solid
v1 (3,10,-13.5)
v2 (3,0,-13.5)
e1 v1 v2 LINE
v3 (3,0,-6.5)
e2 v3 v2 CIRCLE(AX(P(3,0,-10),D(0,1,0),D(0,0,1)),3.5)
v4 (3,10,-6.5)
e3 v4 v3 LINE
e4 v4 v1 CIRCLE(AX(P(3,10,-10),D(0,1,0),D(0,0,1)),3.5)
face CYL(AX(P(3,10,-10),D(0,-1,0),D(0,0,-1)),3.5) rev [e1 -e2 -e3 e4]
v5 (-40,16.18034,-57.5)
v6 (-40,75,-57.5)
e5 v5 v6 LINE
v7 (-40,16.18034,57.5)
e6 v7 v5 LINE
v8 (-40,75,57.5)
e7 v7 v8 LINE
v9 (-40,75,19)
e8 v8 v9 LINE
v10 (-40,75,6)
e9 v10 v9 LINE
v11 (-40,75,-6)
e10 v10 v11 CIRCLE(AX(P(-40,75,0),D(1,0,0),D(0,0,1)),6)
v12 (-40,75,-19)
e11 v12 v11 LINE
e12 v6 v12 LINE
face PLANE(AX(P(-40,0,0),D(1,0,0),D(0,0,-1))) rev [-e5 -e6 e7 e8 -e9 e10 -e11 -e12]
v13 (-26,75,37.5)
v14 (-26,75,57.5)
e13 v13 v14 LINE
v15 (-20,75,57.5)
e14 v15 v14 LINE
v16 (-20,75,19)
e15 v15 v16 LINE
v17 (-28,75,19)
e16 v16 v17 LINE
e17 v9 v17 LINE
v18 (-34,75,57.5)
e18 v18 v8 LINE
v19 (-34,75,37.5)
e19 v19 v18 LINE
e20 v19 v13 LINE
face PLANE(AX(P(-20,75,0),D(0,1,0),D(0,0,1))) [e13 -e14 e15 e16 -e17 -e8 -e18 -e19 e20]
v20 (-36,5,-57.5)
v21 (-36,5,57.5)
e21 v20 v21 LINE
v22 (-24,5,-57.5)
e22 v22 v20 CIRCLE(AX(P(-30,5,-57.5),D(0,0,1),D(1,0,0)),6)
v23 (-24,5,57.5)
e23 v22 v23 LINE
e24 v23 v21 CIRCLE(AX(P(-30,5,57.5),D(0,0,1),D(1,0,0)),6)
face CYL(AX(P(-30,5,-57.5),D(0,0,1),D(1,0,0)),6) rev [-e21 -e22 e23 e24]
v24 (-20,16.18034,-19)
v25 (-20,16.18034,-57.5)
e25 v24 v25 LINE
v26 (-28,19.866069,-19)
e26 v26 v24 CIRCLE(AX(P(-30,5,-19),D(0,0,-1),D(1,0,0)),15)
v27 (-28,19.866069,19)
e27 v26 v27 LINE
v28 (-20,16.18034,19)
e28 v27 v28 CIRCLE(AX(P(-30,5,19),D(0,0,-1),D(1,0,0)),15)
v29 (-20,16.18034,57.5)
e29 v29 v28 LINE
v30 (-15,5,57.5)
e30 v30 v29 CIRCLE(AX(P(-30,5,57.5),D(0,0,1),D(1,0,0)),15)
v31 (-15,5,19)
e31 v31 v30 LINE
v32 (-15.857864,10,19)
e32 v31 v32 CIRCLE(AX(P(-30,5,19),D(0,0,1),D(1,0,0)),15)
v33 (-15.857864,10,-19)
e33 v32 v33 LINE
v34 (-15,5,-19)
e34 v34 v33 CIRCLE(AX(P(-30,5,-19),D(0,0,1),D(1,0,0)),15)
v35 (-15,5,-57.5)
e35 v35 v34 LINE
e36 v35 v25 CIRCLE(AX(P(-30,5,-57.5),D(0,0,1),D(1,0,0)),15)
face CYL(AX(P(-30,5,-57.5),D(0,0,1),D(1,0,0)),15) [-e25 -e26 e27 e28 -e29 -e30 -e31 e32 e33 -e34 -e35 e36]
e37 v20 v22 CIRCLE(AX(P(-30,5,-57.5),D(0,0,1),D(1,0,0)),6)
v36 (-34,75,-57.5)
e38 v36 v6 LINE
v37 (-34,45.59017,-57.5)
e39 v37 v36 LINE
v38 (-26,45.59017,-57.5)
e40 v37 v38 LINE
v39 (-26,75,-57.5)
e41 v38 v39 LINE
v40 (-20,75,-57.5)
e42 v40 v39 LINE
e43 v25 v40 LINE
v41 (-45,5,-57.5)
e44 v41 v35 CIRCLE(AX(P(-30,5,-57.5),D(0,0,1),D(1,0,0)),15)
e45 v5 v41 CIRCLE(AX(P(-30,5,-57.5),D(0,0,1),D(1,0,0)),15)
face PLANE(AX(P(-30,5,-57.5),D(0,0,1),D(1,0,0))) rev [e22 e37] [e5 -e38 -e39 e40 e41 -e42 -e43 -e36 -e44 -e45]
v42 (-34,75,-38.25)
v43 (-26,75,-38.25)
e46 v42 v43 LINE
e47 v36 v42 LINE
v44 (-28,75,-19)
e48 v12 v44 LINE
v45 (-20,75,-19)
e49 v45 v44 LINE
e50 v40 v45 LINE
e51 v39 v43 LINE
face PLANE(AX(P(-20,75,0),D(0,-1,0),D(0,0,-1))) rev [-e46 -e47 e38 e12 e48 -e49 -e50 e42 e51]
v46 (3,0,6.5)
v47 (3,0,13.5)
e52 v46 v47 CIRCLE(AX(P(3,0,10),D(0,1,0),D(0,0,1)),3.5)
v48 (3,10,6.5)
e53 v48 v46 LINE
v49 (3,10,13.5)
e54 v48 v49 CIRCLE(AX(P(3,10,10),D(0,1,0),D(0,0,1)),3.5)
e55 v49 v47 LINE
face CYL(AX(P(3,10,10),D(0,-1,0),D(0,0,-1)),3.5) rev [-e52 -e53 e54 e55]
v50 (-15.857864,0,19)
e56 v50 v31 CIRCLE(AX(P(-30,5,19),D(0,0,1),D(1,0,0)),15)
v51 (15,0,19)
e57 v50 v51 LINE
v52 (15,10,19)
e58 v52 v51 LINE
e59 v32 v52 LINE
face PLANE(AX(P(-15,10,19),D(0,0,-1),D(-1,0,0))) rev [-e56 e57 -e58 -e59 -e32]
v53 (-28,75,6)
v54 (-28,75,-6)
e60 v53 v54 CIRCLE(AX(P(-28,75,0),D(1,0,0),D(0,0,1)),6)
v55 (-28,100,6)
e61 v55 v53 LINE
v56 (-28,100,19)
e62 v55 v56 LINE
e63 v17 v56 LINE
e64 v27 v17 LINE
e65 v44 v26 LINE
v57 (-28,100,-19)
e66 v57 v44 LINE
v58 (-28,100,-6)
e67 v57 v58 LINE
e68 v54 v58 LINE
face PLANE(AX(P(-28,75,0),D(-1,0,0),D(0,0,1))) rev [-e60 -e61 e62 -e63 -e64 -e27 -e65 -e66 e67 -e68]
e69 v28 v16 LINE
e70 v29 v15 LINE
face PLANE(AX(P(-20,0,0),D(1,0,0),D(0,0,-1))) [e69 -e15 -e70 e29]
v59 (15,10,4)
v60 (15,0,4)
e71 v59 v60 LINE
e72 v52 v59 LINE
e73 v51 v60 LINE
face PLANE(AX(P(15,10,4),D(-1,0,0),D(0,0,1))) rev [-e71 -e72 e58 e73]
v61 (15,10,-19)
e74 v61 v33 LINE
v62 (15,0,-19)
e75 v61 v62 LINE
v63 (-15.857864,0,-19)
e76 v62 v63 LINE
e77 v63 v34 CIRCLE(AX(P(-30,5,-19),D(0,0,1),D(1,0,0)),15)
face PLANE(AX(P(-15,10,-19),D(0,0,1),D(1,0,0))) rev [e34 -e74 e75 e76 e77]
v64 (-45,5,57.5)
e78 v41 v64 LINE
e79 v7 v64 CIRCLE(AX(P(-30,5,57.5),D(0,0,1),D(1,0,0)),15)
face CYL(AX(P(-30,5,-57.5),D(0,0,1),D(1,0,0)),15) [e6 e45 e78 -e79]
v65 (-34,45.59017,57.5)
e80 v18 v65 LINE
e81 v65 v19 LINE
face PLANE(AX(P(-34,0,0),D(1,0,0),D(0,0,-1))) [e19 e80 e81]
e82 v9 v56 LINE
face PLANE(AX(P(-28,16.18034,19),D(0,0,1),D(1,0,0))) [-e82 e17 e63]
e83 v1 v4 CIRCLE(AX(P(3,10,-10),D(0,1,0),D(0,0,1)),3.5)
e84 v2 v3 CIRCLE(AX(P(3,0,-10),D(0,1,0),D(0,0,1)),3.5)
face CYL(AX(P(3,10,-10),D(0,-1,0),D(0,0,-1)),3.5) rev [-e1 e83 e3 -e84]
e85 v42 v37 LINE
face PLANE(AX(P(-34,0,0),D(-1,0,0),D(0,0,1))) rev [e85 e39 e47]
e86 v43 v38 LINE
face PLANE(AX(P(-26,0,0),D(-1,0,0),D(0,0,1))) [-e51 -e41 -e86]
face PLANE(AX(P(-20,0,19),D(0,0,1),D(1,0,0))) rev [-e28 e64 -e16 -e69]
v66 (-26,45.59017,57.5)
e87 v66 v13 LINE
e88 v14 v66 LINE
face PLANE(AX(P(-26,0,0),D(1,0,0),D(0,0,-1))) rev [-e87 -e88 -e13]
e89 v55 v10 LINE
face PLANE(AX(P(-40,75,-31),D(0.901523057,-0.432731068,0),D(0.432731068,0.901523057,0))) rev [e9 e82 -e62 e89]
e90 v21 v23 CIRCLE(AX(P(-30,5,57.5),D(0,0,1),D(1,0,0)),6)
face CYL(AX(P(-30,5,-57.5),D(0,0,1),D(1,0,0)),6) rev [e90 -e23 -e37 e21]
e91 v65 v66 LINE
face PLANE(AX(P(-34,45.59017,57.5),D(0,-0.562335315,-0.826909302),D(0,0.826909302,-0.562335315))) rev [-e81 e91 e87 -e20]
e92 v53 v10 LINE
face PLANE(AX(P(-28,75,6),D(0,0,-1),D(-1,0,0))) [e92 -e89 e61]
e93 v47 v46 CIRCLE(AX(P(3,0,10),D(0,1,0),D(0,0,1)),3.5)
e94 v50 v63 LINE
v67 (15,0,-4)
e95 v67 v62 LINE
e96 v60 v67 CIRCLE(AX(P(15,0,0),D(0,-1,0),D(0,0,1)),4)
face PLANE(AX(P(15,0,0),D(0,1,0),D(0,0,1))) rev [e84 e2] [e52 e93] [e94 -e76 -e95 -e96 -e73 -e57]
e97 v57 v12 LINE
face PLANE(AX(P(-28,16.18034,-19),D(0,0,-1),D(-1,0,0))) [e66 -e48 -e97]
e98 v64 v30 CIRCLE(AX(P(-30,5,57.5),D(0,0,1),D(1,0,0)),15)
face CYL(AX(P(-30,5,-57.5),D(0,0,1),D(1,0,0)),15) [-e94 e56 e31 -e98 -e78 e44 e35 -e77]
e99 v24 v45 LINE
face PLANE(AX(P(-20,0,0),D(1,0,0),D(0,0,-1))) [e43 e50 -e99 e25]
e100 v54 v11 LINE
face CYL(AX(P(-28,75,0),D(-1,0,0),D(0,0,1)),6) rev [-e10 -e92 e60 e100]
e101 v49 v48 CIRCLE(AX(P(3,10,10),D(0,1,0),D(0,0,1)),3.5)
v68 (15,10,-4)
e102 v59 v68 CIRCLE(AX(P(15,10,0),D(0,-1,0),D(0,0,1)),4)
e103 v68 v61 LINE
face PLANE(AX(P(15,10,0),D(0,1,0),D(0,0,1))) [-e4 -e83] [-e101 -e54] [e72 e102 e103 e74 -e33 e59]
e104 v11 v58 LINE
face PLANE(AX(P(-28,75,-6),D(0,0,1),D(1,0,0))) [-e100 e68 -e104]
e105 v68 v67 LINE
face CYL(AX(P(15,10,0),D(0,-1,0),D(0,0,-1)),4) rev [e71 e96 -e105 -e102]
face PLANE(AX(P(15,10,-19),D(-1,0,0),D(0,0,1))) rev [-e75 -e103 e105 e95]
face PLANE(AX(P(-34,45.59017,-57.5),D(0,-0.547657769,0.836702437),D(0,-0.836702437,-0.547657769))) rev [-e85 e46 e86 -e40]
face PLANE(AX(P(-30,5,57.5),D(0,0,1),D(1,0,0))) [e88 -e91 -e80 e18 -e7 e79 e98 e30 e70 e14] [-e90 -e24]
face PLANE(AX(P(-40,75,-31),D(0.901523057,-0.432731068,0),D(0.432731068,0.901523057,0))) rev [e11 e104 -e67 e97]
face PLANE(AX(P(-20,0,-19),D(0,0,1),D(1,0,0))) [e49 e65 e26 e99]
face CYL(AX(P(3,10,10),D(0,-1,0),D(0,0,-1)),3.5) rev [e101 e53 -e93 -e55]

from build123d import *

# Parameters (mm, degrees)
BASE_FLANGE_SKETCH_R         = 3.5
BASE_FLANGE_DEPTH            = 10
LOCATING_PAD_SKETCH_W        = 38
LOCATING_PAD_SKETCH_H        = 10
LOCATING_PAD_DEPTH           = 10
HINGE_BARREL_SKETCH_R        = 15
HINGE_BARREL_SKETCH_R_2      = 6
HINGE_BARREL_DEPTH           = 76.5
HINGE_START                  = 38.5
BARREL_EXTENSION_SKETCH_R    = 15
BARREL_EXTENSION_SKETCH_R_2  = 6
HINGE_BARREL_EXTENSION_DEPTH = 38.5
PIN_BORE_SKETCH_R            = 6
HINGE_PIN_BORE_12_DEPTH      = 115
GUIDE_WALLS_SKETCH_W         = 38.5
GUIDE_WALLS_SKETCH_H         = 70
GUIDE_WALLS_DEPTH            = 10
CENTRE_FIN_DEPTH             = 12
FIN_V_SLOT_SKETCH_W          = 12
FIN_V_SLOT_SKETCH_H          = 11.180339887
FIN_V_SLOT_DEPTH             = 50
FIN_RELIEF_CUT_DEPTH         = 50
THROUGH_BORE_SKETCH_R        = 6
THROUGH_BORE_12_DEPTH        = 200
WALL_WINDOWS_DEPTH           = 4


with BuildPart() as part:
    # Base Flange Sketch → Base Flange (new body)
    with BuildSketch(Plane(origin=(0, 0, 0), x_dir=(1, 0, 0), z_dir=(0, 1, 0))):
        with BuildLine():
            Line((15, -4), (15, -19))
            Line((15, -19), (-15, -19))
            Line((-15, -19), (-15, 19))
            Line((-15, 19), (15, 19))
            Line((15, 19), (15, 4))
            ThreePointArc((15, 4), (11, 0), (15, -4))
        make_face()
        with Locations(Location((3, 10, 0), (0, 0, 270))):
            Circle(BASE_FLANGE_SKETCH_R, mode=Mode.SUBTRACT)
        with Locations(Location((3, -10, 0), (0, 0, 270))):
            Circle(BASE_FLANGE_SKETCH_R, mode=Mode.SUBTRACT)
    extrude(amount=BASE_FLANGE_DEPTH)

    # Locating Pad Sketch → Locating Pad (add)
    with BuildSketch(Plane.ZY.offset(15)):
        with Locations((0, 5)):
            Rectangle(LOCATING_PAD_SKETCH_W, LOCATING_PAD_SKETCH_H)
    extrude(amount=LOCATING_PAD_DEPTH)

    # Hinge Barrel Sketch → Hinge Barrel (add)
    with BuildSketch(Plane.XY.offset(19)):
        with Locations((-30, 5)):
            Circle(HINGE_BARREL_SKETCH_R)
        with Locations((-30, 5)):
            Circle(HINGE_BARREL_SKETCH_R_2, mode=Mode.SUBTRACT)
    extrude(amount=-HINGE_BARREL_DEPTH)

    # Barrel Extension Sketch → Hinge Barrel Extension (add)
    with BuildSketch(Plane.XY.offset(19).offset(HINGE_START)):
        with Locations((-30, 5)):
            Circle(BARREL_EXTENSION_SKETCH_R)
        with Locations((-30, 5)):
            Circle(BARREL_EXTENSION_SKETCH_R_2, mode=Mode.SUBTRACT)
    extrude(amount=-HINGE_BARREL_EXTENSION_DEPTH)

    # Pin Bore Sketch → Hinge Pin Bore Ø12 (cut)
    with BuildSketch(Plane.XY.offset(57.5)):
        with Locations((-30, 5)):
            Circle(PIN_BORE_SKETCH_R)
    extrude(amount=-HINGE_PIN_BORE_12_DEPTH, mode=Mode.SUBTRACT)

    # Guide Walls Sketch → Guide Walls (add, symmetric)
    with BuildSketch(Plane(origin=(-30, 0, 0), x_dir=(0, 0, -1), z_dir=(1, 0, 0))):
        with Locations((38.25, 40)):
            Rectangle(GUIDE_WALLS_SKETCH_W, GUIDE_WALLS_SKETCH_H)
        with Locations((-38.25, 40)):
            Rectangle(GUIDE_WALLS_SKETCH_W, GUIDE_WALLS_SKETCH_H)
    extrude(amount=GUIDE_WALLS_DEPTH, both=True)

    # Centre Fin Sketch → Centre Fin (add)
    with BuildSketch(Plane.ZY.offset(40)):
        with BuildLine():
            Line((-19, 16.180339887), (19, 16.180339887))
            Line((19, 16.180339887), (19, 111.180339887))
            Line((19, 111.180339887), (6, 111.180339887))
            Line((6, 111.180339887), (6, 75))
            ThreePointArc((6, 75), (0, 69), (-6, 75))
            Line((-6, 75), (-6, 111.180339887))
            Line((-6, 111.180339887), (-19, 111.180339887))
            Line((-19, 111.180339887), (-19, 16.180339887))
        make_face()
    extrude(amount=-CENTRE_FIN_DEPTH)

    # Fin V-Slot Sketch → Fin V-Slot (cut)
    with BuildSketch(Plane.XY.offset(19)):
        with Locations((-34, 105.590169944)):
            Rectangle(FIN_V_SLOT_SKETCH_W, FIN_V_SLOT_SKETCH_H)
    extrude(amount=-FIN_V_SLOT_DEPTH, mode=Mode.SUBTRACT)

    # Fin Relief Sketch → Fin Relief Cut (cut)
    with BuildSketch(Plane.XY.offset(19)):
        Polygon((-40, 75), (-28, 100), (-40, 100), align=None)
    extrude(amount=-FIN_RELIEF_CUT_DEPTH, mode=Mode.SUBTRACT)

    # Through Bore Sketch → Through Bore Ø12 (cut)
    with BuildSketch(Plane.XY.offset(57.5)):
        with Locations((-30, 5)):
            Circle(THROUGH_BORE_SKETCH_R)
    extrude(amount=-THROUGH_BORE_12_DEPTH, mode=Mode.SUBTRACT)

    # Wall Window Sketch → Wall Windows (cut, symmetric)
    with BuildSketch(Plane(origin=(-30, 0, 0), x_dir=(0, 0, -1), z_dir=(1, 0, 0))):
        Polygon((57.5, 75), (38.25, 75), (57.5, 45.590169944), align=None)
        Polygon((-57.5, 75), (-57.5, 45.590169944), (-37.5, 75), align=None)
    extrude(amount=WALL_WINDOWS_DEPTH, both=True, mode=Mode.SUBTRACT)


solid = part.part
